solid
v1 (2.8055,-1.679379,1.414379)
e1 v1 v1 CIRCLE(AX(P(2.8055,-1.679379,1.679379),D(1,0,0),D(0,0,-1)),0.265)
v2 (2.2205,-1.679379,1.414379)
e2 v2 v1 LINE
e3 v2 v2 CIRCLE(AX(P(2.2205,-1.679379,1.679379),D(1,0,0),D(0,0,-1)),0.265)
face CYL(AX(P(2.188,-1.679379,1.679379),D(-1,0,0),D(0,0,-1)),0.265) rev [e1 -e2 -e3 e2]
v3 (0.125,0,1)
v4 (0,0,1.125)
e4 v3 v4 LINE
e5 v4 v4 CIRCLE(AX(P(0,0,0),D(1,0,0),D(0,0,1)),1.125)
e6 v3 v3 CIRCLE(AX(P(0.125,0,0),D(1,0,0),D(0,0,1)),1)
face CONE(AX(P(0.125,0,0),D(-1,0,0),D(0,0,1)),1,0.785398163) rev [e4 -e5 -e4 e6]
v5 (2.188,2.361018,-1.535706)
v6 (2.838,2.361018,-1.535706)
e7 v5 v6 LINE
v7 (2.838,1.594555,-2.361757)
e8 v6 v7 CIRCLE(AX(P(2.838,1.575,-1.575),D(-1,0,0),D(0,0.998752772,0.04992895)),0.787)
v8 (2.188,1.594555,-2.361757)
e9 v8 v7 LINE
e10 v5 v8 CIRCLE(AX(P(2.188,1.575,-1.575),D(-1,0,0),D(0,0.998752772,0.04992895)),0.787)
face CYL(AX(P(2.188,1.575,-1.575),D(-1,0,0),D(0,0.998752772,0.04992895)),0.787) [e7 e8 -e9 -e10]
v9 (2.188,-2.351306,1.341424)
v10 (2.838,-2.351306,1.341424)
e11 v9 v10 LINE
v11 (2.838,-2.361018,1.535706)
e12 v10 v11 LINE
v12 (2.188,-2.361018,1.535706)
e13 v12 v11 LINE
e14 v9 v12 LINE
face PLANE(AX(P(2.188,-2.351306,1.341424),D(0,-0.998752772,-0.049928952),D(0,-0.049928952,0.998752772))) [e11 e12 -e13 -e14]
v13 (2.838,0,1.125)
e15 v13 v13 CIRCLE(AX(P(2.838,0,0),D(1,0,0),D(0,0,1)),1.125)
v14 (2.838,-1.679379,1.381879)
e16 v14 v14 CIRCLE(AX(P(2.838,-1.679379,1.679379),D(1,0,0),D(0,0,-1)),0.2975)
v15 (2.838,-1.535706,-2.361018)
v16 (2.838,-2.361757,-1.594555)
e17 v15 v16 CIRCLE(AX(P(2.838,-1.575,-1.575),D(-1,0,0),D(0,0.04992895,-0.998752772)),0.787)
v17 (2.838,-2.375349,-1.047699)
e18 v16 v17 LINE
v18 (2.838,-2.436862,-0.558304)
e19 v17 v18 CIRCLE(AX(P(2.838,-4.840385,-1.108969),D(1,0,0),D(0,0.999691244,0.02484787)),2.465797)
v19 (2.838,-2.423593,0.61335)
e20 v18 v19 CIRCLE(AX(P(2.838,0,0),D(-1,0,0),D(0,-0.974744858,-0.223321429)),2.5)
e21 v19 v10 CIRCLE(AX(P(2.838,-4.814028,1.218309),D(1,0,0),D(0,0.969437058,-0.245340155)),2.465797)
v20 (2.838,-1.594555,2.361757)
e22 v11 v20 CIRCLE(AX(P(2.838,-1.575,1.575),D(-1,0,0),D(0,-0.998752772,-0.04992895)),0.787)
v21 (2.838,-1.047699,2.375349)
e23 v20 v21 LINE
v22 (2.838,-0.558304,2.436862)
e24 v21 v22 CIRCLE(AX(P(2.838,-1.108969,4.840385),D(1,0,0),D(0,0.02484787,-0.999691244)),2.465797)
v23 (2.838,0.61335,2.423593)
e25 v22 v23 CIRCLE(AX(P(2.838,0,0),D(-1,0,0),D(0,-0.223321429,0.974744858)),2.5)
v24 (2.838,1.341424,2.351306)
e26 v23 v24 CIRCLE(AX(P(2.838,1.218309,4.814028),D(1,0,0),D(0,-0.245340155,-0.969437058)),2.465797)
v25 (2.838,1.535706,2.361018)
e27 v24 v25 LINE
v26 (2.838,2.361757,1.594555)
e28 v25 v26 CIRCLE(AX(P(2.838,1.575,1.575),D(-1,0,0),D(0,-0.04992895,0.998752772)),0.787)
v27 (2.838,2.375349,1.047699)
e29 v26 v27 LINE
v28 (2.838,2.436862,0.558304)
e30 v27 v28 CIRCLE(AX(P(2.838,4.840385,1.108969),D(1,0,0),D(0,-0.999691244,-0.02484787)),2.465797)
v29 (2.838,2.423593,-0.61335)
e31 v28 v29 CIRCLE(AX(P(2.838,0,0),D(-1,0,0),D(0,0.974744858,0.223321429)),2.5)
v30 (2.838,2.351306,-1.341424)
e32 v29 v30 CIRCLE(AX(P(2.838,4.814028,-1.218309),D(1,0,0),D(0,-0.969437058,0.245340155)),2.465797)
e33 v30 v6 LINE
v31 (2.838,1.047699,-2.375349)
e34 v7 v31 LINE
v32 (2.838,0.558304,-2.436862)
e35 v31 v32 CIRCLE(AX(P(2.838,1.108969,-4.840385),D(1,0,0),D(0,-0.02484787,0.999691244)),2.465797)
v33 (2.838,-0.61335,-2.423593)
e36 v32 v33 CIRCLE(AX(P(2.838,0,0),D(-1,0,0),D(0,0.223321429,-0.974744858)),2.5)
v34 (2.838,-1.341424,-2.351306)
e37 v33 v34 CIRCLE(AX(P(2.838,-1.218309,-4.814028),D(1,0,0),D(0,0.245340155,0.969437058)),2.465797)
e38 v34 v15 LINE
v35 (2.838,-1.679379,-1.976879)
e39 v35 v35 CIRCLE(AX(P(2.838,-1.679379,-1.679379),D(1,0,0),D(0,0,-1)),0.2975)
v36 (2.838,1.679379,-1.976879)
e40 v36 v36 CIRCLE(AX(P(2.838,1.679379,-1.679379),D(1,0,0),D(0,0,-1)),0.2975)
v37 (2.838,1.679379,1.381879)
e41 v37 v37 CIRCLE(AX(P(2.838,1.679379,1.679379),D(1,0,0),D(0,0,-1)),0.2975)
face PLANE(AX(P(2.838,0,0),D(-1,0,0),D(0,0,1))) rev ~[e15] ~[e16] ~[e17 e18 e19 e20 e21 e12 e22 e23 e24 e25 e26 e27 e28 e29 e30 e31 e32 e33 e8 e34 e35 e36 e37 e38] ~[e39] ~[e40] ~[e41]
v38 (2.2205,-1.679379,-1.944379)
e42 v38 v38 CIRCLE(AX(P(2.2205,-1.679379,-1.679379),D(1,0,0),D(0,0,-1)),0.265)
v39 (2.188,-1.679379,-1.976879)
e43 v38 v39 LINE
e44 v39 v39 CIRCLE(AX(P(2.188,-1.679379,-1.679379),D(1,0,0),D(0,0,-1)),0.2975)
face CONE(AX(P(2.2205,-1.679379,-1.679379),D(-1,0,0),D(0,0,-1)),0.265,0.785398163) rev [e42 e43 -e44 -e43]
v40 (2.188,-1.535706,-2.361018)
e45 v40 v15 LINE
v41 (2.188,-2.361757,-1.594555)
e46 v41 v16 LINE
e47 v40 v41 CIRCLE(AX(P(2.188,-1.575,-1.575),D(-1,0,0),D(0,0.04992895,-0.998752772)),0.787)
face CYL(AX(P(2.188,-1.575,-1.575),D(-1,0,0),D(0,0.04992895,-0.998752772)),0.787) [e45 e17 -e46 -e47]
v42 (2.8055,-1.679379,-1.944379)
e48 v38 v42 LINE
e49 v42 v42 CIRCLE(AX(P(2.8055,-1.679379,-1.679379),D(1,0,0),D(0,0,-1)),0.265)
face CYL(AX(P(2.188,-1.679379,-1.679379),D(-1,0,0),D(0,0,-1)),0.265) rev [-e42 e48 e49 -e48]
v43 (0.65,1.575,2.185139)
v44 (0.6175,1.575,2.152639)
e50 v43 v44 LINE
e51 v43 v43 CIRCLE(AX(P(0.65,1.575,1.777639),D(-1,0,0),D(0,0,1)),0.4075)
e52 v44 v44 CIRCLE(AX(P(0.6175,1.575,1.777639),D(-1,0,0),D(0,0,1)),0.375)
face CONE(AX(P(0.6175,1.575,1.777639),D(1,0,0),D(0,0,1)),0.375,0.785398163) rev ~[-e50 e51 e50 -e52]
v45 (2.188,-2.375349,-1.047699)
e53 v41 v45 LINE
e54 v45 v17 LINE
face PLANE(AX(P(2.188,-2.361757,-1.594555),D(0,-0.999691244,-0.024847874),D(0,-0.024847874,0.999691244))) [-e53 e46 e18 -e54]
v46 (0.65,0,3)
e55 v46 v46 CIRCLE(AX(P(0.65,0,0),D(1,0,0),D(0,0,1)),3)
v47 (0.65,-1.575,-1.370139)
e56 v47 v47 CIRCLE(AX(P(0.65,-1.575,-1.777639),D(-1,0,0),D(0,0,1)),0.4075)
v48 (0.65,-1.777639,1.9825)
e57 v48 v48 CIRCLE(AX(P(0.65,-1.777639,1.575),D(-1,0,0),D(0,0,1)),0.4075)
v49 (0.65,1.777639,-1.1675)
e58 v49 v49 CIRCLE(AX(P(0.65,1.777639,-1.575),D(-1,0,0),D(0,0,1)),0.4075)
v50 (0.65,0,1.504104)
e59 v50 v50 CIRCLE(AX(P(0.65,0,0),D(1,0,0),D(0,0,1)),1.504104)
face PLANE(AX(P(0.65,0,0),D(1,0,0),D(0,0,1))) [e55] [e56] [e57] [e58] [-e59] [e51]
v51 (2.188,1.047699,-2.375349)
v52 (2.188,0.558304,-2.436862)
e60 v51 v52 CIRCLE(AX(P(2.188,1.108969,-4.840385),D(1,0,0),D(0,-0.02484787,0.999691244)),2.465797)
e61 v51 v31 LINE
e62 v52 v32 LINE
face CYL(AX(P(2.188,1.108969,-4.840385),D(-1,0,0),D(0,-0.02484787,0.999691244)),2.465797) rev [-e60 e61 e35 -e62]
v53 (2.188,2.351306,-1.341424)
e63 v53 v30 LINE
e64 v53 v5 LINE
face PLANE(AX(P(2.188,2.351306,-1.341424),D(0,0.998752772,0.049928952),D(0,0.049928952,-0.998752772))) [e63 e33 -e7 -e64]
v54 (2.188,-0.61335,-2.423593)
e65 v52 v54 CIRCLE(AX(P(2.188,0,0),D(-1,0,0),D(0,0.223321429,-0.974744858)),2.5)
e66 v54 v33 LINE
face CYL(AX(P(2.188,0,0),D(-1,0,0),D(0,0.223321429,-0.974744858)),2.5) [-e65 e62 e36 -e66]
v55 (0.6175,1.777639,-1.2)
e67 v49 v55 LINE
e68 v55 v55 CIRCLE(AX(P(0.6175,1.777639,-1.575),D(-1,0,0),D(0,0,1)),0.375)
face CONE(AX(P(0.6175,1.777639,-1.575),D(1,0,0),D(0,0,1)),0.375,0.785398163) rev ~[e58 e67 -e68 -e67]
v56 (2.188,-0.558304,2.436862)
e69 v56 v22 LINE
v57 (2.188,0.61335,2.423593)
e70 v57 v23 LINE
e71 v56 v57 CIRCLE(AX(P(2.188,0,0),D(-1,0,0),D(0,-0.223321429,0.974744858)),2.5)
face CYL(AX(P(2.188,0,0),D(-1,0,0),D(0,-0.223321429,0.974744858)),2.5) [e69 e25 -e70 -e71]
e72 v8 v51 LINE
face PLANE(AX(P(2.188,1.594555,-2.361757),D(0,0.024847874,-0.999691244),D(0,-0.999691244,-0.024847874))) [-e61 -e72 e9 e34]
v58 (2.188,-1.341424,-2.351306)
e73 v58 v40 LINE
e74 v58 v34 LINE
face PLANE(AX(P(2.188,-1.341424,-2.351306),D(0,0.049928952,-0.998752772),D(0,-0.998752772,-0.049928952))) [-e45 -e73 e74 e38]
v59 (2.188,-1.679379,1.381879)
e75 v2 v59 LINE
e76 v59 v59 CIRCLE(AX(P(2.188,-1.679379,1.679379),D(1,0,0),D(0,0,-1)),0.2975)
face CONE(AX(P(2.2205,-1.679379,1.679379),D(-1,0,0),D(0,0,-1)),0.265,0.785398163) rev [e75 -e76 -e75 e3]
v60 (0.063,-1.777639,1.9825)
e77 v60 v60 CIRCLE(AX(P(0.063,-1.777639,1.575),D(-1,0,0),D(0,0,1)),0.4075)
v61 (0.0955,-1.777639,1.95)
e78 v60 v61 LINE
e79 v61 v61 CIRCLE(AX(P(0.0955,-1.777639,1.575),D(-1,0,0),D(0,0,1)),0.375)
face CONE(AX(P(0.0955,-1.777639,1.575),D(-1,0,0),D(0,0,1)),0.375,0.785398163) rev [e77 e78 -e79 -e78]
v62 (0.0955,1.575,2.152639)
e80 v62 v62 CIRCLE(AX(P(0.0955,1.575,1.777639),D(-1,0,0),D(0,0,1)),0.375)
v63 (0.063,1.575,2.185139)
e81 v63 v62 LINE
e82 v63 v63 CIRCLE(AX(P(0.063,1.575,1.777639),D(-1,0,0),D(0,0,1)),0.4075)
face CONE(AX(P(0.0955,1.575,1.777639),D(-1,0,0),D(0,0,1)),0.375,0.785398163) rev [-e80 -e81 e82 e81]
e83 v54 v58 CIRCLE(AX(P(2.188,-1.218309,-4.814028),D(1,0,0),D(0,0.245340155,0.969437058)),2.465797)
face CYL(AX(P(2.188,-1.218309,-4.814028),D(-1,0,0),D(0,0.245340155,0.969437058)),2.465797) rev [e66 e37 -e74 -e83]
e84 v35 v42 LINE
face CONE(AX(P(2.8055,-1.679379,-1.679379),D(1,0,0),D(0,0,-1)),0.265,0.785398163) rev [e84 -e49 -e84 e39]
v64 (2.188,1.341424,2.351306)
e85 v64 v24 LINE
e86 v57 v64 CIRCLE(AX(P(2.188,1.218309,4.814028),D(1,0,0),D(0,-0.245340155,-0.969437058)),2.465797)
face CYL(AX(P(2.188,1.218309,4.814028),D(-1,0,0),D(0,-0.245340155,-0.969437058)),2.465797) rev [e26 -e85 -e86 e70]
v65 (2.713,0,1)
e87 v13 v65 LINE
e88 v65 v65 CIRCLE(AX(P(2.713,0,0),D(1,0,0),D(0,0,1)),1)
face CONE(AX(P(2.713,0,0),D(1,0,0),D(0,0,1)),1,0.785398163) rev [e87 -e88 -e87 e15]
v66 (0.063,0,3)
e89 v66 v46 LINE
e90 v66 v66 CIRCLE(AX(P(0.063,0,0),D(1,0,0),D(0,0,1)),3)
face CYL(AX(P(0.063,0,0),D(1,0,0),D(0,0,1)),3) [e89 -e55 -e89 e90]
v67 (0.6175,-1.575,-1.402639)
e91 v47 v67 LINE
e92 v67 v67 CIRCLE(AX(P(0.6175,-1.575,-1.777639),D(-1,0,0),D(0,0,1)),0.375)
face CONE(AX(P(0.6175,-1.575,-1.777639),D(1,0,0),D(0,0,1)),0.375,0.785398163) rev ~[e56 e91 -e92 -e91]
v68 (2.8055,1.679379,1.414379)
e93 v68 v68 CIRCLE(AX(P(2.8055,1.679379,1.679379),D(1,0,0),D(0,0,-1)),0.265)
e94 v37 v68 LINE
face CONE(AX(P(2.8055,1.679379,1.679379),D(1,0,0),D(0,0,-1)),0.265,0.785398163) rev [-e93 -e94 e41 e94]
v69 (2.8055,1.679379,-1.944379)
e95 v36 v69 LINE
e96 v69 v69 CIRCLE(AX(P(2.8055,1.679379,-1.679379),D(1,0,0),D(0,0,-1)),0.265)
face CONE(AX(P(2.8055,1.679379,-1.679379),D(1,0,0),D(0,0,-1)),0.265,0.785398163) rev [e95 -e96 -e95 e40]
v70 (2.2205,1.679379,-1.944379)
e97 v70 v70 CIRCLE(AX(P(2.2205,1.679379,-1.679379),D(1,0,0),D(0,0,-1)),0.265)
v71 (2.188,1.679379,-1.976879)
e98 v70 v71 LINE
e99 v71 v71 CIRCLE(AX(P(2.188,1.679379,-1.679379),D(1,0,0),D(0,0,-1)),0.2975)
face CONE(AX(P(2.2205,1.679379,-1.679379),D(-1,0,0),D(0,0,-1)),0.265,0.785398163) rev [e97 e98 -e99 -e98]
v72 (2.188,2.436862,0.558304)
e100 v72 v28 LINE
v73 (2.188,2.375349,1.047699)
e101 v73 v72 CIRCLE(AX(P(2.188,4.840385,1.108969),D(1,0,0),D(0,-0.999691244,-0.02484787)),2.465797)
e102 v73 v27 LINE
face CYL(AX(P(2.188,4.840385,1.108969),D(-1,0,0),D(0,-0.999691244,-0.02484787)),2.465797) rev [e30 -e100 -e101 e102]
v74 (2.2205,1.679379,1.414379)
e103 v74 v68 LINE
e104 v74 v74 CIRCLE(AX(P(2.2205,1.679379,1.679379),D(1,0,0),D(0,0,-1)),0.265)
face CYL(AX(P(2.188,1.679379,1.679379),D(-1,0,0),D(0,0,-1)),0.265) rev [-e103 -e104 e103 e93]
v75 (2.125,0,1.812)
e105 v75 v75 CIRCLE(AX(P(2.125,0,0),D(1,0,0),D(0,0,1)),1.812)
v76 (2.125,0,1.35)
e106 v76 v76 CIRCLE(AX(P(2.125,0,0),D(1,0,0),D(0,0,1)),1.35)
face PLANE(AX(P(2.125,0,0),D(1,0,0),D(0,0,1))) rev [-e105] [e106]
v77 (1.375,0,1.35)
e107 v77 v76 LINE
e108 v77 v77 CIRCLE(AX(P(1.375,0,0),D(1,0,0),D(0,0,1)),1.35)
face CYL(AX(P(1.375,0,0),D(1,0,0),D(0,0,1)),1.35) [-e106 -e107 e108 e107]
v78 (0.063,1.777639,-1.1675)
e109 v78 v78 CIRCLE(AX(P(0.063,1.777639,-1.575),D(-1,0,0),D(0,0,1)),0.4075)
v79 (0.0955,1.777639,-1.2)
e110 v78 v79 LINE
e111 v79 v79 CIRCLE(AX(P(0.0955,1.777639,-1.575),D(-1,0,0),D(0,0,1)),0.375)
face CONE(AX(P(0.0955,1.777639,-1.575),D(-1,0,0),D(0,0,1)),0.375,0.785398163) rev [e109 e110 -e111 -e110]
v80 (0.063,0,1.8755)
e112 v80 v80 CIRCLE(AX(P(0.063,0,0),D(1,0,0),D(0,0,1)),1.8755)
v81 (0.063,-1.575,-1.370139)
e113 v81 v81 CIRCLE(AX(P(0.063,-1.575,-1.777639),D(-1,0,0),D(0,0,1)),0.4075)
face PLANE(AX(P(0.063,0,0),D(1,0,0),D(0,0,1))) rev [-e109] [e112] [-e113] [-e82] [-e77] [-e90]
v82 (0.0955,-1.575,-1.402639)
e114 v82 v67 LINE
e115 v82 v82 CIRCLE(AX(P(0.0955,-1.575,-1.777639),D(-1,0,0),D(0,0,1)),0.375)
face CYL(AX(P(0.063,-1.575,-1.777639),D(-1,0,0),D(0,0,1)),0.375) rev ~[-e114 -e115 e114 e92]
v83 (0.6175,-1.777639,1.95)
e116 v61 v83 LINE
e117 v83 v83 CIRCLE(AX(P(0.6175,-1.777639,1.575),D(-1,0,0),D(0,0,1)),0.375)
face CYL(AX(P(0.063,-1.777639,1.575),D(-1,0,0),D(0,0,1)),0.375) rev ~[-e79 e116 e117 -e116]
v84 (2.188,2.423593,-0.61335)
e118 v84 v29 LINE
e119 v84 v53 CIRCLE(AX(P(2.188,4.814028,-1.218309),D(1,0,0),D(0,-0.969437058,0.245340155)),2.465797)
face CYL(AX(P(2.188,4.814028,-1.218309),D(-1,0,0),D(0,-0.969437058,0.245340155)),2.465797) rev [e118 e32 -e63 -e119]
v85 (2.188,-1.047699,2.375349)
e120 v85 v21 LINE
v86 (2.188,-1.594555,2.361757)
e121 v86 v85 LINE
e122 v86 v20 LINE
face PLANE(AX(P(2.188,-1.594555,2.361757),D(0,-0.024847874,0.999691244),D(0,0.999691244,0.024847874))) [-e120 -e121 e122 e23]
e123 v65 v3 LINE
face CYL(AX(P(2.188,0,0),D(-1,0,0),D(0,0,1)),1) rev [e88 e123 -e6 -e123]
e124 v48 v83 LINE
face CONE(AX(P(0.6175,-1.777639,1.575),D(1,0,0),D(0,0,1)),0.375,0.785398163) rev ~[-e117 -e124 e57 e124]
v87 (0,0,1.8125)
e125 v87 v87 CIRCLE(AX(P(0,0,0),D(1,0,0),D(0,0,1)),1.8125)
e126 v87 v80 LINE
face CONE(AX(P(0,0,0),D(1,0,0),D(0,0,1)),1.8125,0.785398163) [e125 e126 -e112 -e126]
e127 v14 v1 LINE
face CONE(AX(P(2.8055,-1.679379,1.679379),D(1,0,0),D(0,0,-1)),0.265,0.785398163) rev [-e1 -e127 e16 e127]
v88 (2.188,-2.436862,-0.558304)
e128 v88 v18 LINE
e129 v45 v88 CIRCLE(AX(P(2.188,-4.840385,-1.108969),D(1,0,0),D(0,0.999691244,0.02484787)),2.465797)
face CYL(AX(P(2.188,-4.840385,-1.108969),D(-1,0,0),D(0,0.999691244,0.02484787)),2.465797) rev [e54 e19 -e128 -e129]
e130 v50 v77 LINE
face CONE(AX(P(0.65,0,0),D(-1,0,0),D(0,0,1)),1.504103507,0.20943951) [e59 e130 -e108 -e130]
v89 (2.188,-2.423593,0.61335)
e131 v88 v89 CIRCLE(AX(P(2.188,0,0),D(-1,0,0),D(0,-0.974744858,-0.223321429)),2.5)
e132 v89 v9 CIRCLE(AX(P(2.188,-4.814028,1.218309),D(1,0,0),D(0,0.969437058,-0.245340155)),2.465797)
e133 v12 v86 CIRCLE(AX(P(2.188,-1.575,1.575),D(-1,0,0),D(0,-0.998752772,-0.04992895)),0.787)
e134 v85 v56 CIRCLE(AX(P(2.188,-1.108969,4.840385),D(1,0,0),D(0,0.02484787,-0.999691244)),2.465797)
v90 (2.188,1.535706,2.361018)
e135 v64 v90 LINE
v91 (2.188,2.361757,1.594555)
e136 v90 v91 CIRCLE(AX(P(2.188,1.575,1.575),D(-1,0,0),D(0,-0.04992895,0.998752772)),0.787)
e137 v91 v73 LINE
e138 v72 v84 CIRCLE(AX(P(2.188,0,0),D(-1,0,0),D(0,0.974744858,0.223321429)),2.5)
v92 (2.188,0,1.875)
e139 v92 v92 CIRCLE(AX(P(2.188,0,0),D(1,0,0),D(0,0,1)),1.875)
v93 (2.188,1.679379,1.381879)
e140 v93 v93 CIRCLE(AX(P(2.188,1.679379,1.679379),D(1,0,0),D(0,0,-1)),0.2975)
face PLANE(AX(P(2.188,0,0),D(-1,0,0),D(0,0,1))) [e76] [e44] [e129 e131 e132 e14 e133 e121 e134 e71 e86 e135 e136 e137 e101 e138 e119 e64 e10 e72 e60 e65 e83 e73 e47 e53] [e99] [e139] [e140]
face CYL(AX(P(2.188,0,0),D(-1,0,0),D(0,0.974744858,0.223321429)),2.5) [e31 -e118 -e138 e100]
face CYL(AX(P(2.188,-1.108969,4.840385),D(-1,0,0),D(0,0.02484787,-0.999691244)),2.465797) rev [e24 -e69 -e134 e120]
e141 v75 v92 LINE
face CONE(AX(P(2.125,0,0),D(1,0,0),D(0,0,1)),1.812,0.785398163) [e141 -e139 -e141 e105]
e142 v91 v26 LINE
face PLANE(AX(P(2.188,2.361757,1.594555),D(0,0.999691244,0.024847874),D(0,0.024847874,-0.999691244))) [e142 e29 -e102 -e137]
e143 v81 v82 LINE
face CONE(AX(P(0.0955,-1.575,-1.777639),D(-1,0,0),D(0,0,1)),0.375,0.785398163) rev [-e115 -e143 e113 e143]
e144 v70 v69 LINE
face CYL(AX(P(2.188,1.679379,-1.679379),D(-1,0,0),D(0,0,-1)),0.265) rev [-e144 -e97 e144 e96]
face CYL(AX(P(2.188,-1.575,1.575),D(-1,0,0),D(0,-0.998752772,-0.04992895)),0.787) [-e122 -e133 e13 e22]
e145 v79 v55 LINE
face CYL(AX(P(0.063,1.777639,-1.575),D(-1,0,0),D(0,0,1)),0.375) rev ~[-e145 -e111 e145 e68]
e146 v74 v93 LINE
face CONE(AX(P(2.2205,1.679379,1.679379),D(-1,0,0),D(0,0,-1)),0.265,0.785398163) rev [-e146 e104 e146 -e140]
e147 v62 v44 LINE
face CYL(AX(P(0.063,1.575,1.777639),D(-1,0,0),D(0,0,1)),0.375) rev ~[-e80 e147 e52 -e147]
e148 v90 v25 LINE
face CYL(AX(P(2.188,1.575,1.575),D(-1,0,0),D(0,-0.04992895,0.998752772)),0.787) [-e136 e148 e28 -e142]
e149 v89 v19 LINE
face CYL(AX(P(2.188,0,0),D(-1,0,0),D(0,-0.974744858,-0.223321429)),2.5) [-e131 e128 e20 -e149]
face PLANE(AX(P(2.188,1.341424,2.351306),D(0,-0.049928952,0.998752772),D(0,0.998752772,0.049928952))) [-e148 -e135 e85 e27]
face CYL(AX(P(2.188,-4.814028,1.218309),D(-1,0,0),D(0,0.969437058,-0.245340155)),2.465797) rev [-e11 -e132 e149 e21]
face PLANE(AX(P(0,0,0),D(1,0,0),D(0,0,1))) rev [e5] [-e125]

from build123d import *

# Parameters (mm, degrees)
SQUARE_FLANGE_SKETCH_R           = 1
SQUARE_FLANGE_SKETCH_R_2         = 0.265
SQUARE_OUTLET_FLANGE_DEPTH       = 0.65
ROUND_FLANGE_HOLES_SKETCH_R      = 0.375
ROUND_FLANGE_HOLES_4X_0_75_DEPTH = 0.65
ROUND_FLANGE_HOLE_CHAMFERS_SIZE  = 0.0325
SQUARE_FLANGE_CHAMFERS_SIZE      = 0.0325
HOUSING_EDGE_CHAMFERS_SIZE       = 0.125


with BuildPart() as part:
    # Housing Profile Sketch → Housing Body Revolve (revolve)
    with BuildSketch(Plane.XY, mode=Mode.PRIVATE) as housing_body_revolve_sk:
        Polygon((0, 1), (0, 1.8125), (0.063, 1.8755), (0.063, 3), (0.65, 3), (0.65, 1.504103507), (1.375, 1.35), (2.125, 1.35), (2.125, 1.812), (2.188, 1.875), (2.188, 1), align=None)
    revolve(housing_body_revolve_sk.sketch.rotate(Axis((0, 0, 0), (1, 0, 0)), 90), axis=Axis((0, 0, 0), (1, 0, 0)))

    # Square Flange Sketch → Square Outlet Flange (add)
    with BuildSketch(Plane(origin=(2.188, 0, 0), x_dir=(0, 0, -1), z_dir=(1, 0, 0))):
        with BuildLine():
            Line((-1.594555277, 2.361757009), (-1.047699115, 2.375349419))
            ThreePointArc((-1.047699115, 2.375349419), (-0.801459389, 2.393837984), (-0.558303573, 2.436862146))
            ThreePointArc((-0.558303573, 2.436862146), (0.0283118, 2.499839683), (0.613350393, 2.423592642))
            ThreePointArc((0.613350393, 2.423592642), (0.974691231, 2.360294751), (1.341424141, 2.351306033))
            Line((1.341424141, 2.351306033), (1.535705916, 2.361018432))
            ThreePointArc((1.535705916, 2.361018432), (2.110295851, 2.15191191), (2.361757009, 1.594555277))
            Line((2.361757009, 1.594555277), (2.375349419, 1.047699115))
            ThreePointArc((2.375349419, 1.047699115), (2.393837984, 0.801459389), (2.436862146, 0.558303573))
            ThreePointArc((2.436862146, 0.558303573), (2.499839683, -0.0283118), (2.423592642, -0.613350393))
            ThreePointArc((2.423592642, -0.613350393), (2.360294751, -0.974691231), (2.351306033, -1.341424141))
            Line((2.351306033, -1.341424141), (2.361018432, -1.535705916))
            ThreePointArc((2.361018432, -1.535705916), (2.15191191, -2.110295851), (1.594555277, -2.361757009))
            Line((1.594555277, -2.361757009), (1.047699115, -2.375349419))
            ThreePointArc((1.047699115, -2.375349419), (0.801459389, -2.393837984), (0.558303573, -2.436862146))
            ThreePointArc((0.558303573, -2.436862146), (-0.0283118, -2.499839683), (-0.613350393, -2.423592642))
            ThreePointArc((-0.613350393, -2.423592642), (-0.974691231, -2.360294751), (-1.341424141, -2.351306033))
            Line((-1.341424141, -2.351306033), (-1.535705916, -2.361018432))
            ThreePointArc((-1.535705916, -2.361018432), (-2.110295851, -2.15191191), (-2.361757009, -1.594555277))
            Line((-2.361757009, -1.594555277), (-2.375349419, -1.047699115))
            ThreePointArc((-2.375349419, -1.047699115), (-2.393837984, -0.801459389), (-2.436862146, -0.558303573))
            ThreePointArc((-2.436862146, -0.558303573), (-2.499839683, 0.0283118), (-2.423592642, 0.613350393))
            ThreePointArc((-2.423592642, 0.613350393), (-2.360294751, 0.974691231), (-2.351306033, 1.341424141))
            Line((-2.351306033, 1.341424141), (-2.361018432, 1.535705916))
            ThreePointArc((-2.361018432, 1.535705916), (-2.15191191, 2.110295851), (-1.594555277, 2.361757009))
        make_face()
        with Locations(Location((0, 0, 0), (0, 0, 180))):
            Circle(SQUARE_FLANGE_SKETCH_R, mode=Mode.SUBTRACT)
        with Locations((-1.679378605, 1.679378605)):
            Circle(SQUARE_FLANGE_SKETCH_R_2, mode=Mode.SUBTRACT)
        with Locations((1.679378605, 1.679378605)):
            Circle(SQUARE_FLANGE_SKETCH_R_2, mode=Mode.SUBTRACT)
        with Locations((1.679378605, -1.679378605)):
            Circle(SQUARE_FLANGE_SKETCH_R_2, mode=Mode.SUBTRACT)
        with Locations((-1.679378605, -1.679378605)):
            Circle(SQUARE_FLANGE_SKETCH_R_2, mode=Mode.SUBTRACT)
    extrude(amount=SQUARE_OUTLET_FLANGE_DEPTH)

    # Round Flange Holes Sketch → Round Flange Holes 4xØ0.75 (cut)
    with BuildSketch(Plane.ZY.offset(-0.063)):
        with Locations((-1.575, 1.777638883)):
            Circle(ROUND_FLANGE_HOLES_SKETCH_R)
        with Locations((1.777638883, 1.575)):
            Circle(ROUND_FLANGE_HOLES_SKETCH_R)
        with Locations((1.575, -1.777638883)):
            Circle(ROUND_FLANGE_HOLES_SKETCH_R)
        with Locations((-1.777638883, -1.575)):
            Circle(ROUND_FLANGE_HOLES_SKETCH_R)
    extrude(amount=-ROUND_FLANGE_HOLES_4X_0_75_DEPTH, mode=Mode.SUBTRACT)

    # Round Flange Hole Chamfers
    round_flange_hole_chamfers_edges = [part.edges().sort_by_distance(p)[0] for p in [
        (0.65, -1.777638883, 1.2),
        (0.063, -1.777638883, 1.2),
        (0.65, 1.575, 1.402638883),
        (0.063, 1.575, 1.402638883),
        (0.65, 1.777638883, -1.95),
        (0.063, 1.777638883, -1.95),
        (0.65, -1.575, -2.152638883),
        (0.063, -1.575, -2.152638883),
    ]]
    chamfer(round_flange_hole_chamfers_edges, length=ROUND_FLANGE_HOLE_CHAMFERS_SIZE)

    # Square Flange Chamfers
    square_flange_chamfers_edges = [part.edges().sort_by_distance(p)[0] for p in [
        (2.188, 1.679378605, 1.944378605),
        (2.188, 1.679378605, -1.414378605),
        (2.188, -1.679378605, -1.414378605),
        (2.188, -1.679378605, 1.944378605),
        (2.838, 1.679378605, 1.944378605),
        (2.838, 1.679378605, -1.414378605),
        (2.838, -1.679378605, -1.414378605),
        (2.838, -1.679378605, 1.944378605),
    ]]
    chamfer(square_flange_chamfers_edges, length=SQUARE_FLANGE_CHAMFERS_SIZE)

    # Housing Edge Chamfers
    housing_edge_chamfers_edges = [part.edges().sort_by_distance(p)[0] for p in [
        (0, 0, -1),
        (2.838, 0, -1),
    ]]
    chamfer(housing_edge_chamfers_edges, length=HOUSING_EDGE_CHAMFERS_SIZE)


solid = part.part
